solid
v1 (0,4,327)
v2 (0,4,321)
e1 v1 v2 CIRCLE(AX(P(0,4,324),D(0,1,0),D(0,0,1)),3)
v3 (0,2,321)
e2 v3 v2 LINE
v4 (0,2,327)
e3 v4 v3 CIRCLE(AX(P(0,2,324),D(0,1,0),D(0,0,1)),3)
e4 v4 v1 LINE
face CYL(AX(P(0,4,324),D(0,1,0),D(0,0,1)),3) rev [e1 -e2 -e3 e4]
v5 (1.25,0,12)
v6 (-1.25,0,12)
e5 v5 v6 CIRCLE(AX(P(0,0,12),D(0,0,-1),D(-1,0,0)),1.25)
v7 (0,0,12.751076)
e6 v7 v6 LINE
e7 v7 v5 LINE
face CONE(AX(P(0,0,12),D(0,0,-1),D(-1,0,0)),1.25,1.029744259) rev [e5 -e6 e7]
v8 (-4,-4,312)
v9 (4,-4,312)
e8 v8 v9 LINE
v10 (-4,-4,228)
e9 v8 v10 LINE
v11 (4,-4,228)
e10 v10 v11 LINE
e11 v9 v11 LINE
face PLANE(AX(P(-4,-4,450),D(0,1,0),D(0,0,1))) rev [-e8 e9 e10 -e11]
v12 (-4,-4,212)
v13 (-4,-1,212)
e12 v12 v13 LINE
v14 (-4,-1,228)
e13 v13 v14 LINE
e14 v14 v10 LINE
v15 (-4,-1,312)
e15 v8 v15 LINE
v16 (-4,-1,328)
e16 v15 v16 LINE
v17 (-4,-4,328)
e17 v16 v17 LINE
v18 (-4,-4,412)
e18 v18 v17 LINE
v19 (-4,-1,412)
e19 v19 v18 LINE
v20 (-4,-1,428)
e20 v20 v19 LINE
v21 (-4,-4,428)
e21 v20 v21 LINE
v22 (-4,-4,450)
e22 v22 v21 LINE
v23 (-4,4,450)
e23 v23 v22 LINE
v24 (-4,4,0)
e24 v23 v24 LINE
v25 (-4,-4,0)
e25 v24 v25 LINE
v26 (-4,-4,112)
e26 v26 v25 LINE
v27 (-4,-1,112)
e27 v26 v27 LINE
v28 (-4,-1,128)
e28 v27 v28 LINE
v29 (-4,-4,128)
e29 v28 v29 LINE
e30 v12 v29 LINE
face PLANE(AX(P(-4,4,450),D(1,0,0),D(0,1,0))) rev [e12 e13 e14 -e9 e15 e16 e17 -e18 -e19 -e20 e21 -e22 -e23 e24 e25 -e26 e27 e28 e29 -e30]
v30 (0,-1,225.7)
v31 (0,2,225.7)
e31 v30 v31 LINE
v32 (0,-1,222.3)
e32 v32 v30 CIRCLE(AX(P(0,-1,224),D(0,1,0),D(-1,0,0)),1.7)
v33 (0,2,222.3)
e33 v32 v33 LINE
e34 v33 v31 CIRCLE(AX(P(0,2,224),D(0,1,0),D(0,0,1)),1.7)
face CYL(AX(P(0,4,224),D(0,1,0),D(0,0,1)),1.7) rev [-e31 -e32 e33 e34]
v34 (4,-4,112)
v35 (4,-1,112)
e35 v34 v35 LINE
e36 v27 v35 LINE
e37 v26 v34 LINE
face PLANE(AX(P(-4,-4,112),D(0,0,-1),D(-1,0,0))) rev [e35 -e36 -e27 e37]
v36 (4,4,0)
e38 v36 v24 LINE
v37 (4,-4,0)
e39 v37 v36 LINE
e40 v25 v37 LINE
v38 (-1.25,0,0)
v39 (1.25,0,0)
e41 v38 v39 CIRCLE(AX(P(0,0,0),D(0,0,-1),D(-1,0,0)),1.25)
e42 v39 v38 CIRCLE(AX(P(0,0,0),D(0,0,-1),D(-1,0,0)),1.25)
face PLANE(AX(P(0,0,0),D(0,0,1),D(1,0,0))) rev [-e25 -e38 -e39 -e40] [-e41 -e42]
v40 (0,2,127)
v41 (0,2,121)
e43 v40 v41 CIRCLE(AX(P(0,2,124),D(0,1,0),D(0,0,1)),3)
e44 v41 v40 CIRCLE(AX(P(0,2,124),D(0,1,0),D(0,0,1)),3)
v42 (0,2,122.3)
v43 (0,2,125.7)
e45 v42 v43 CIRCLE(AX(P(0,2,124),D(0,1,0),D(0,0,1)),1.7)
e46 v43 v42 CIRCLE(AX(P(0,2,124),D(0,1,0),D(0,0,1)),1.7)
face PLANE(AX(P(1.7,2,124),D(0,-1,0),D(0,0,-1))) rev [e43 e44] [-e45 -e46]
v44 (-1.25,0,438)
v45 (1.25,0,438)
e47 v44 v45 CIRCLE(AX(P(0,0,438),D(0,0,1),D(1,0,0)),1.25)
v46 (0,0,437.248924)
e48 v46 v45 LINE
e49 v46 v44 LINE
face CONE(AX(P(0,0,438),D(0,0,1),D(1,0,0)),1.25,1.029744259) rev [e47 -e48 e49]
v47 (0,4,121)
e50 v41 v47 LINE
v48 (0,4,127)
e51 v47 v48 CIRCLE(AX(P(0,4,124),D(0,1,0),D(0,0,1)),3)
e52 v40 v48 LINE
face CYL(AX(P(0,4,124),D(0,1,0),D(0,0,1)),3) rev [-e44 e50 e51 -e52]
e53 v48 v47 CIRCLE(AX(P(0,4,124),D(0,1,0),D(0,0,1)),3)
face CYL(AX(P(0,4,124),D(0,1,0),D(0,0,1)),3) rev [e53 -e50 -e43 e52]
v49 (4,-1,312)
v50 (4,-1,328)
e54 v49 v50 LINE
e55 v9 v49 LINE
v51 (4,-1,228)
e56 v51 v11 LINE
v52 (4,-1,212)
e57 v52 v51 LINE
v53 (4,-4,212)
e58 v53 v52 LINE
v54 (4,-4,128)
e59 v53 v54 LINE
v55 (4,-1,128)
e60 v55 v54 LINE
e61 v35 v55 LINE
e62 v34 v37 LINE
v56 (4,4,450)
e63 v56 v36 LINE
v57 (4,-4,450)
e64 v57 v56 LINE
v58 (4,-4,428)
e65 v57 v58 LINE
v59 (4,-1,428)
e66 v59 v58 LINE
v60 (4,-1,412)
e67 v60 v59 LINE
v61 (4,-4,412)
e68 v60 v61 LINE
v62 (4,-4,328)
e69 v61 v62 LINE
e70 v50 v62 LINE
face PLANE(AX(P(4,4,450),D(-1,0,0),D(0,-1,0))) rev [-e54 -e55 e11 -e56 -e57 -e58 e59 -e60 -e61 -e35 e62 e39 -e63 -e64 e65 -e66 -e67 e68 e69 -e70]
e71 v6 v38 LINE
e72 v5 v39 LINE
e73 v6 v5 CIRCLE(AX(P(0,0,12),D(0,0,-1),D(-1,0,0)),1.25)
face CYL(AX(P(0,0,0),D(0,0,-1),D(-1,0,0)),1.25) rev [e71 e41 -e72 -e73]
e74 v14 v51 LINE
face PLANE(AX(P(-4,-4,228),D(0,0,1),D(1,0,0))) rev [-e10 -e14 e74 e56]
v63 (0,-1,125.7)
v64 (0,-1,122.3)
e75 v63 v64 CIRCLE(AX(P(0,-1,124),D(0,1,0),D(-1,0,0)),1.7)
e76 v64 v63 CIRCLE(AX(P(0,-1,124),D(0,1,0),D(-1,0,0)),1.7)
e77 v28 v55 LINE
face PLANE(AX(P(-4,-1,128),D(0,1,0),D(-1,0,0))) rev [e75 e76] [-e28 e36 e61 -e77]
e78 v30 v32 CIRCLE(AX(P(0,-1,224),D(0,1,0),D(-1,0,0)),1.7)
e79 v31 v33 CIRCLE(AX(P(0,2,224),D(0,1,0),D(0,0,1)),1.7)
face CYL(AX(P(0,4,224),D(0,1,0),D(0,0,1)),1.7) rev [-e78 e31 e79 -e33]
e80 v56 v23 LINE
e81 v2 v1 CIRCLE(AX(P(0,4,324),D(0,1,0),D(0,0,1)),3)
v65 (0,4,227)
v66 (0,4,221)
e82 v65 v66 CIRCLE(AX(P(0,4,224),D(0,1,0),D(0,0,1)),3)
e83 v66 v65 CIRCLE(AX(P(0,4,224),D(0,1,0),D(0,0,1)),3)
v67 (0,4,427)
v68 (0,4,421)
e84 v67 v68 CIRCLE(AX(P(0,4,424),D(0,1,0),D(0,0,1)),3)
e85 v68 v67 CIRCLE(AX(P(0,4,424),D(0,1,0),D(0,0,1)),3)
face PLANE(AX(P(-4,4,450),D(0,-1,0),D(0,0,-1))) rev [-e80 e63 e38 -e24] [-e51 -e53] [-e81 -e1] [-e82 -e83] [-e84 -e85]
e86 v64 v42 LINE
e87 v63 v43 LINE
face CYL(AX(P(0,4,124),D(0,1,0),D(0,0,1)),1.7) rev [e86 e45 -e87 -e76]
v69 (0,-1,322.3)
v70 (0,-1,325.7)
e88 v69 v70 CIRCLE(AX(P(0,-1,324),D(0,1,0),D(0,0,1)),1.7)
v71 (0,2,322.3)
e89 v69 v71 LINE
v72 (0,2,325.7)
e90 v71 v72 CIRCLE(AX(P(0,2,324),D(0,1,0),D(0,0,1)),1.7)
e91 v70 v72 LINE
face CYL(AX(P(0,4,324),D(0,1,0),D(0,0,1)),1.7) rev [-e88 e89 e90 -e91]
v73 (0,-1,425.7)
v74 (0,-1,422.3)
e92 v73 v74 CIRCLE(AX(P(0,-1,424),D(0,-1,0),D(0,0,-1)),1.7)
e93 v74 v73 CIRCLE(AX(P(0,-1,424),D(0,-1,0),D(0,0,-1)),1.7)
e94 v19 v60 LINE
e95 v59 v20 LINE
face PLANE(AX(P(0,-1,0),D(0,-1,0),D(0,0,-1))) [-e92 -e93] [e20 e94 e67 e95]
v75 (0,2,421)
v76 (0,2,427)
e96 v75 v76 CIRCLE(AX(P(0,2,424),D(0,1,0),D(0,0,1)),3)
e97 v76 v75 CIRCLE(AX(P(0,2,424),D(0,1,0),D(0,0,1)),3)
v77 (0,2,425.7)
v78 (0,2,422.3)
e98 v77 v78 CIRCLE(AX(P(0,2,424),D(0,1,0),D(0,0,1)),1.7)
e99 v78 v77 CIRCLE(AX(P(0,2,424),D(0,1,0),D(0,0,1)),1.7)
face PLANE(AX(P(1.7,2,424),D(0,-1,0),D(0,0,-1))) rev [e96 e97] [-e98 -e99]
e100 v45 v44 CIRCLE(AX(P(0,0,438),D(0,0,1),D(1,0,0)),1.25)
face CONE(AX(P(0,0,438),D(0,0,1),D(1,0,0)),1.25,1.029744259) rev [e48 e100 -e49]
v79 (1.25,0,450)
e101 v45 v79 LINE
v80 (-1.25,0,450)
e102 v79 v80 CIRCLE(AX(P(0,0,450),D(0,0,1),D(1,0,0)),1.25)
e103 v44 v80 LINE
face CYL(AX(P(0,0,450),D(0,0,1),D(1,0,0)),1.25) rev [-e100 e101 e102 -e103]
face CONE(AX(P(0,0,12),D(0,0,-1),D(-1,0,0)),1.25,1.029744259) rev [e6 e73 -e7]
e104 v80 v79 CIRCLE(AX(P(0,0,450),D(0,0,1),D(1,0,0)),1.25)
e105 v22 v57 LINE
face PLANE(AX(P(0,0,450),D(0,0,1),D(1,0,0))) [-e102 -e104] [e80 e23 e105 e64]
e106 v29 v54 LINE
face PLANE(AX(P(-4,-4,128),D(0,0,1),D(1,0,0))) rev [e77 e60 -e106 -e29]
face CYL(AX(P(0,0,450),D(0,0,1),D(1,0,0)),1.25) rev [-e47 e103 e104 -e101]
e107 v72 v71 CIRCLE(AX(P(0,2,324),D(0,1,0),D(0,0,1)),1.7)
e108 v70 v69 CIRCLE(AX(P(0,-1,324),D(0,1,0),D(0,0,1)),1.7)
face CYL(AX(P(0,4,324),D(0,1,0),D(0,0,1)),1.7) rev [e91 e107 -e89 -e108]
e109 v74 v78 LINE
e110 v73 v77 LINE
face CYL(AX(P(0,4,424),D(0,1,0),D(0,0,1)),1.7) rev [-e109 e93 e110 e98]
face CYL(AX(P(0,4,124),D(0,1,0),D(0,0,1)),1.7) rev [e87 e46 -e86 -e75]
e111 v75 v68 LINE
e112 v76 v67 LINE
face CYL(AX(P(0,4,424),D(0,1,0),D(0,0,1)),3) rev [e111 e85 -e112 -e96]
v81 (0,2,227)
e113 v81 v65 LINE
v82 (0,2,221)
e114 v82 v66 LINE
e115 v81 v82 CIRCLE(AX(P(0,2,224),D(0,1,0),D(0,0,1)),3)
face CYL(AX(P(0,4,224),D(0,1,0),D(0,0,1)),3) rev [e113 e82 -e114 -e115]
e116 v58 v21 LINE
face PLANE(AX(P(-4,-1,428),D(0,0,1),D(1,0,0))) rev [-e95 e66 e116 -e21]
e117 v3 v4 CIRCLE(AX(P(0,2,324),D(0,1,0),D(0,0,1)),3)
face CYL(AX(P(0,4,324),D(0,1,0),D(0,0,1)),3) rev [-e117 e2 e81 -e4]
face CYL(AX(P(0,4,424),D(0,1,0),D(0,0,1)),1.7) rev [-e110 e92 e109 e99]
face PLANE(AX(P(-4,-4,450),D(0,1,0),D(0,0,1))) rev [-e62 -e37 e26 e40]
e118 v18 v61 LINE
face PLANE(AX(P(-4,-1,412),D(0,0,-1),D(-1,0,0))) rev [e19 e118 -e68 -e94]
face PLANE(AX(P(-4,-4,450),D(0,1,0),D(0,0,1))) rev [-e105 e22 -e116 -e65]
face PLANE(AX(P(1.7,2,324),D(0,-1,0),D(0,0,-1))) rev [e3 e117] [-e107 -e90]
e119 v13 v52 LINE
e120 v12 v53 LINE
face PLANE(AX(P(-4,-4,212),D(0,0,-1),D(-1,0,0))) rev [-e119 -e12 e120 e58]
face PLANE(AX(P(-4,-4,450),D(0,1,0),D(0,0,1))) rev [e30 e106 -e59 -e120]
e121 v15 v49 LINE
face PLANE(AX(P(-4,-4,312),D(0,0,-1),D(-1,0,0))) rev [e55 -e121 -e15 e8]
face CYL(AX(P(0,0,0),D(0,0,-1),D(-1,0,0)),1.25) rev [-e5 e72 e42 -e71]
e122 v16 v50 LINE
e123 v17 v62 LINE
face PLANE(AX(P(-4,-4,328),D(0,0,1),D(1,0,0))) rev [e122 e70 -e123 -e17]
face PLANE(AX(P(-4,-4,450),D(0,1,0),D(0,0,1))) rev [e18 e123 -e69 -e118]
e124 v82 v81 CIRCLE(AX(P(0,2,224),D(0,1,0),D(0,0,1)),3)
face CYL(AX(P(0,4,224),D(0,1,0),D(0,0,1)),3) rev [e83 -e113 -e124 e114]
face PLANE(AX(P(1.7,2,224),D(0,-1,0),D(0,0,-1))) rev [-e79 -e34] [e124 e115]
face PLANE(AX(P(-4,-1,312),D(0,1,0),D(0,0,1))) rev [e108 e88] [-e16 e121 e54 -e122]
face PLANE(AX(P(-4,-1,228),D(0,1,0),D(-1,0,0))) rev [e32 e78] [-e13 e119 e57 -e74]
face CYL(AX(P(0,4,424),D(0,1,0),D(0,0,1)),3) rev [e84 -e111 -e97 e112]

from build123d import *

# Parameters (mm, degrees)
SKETCH_1_W                = 8
SKETCH_1_H                = 8
EXTRUDE_1_DEPTH           = 450
SKETCH_3_W                = 8
SKETCH_3_H                = 16
CUT_EXTRUDE_2_DEPTH       = 3
HOLE_WIZARD_M3_1_D        = 2.5
HOLE_WIZARD_M3_1_DEPTH    = 12
HOLE_WIZARD_M3_1_TIP      = 0.751075774
HOLE_WIZARD_M3_2_D        = 2.5
HOLE_WIZARD_M3_2_DEPTH    = 12
HOLE_WIZARD_M3_2_TIP      = 0.751075774
SKETCH_10_W               = 16
SKETCH_10_H               = 3
CUT_EXTRUDE_3_DEPTH       = 451.088880111
HOLE_WIZARD_1_D           = 3.4
HOLE_WIZARD_1_CBORE_D     = 6
HOLE_WIZARD_1_CBORE_DEPTH = 2


with BuildPart() as part:
    # 草图1 → 凸台-拉伸1 (new body)
    with BuildSketch(Plane.XY):
        Rectangle(SKETCH_1_W, SKETCH_1_H)
    extrude(amount=EXTRUDE_1_DEPTH)

    # 草图3 → 切除-拉伸2 (cut)
    with BuildSketch(Plane.XZ.offset(4)):
        with Locations((0, 420)):
            Rectangle(SKETCH_3_W, SKETCH_3_H)
    extrude(amount=-CUT_EXTRUDE_2_DEPTH, mode=Mode.SUBTRACT)

    # M3 螺纹孔1
    with Locations(Plane(origin=(0, 0, 0), x_dir=(-1, 0, 0), z_dir=(0, 0, -1))):
        with Locations((0, 0)):
            Hole(HOLE_WIZARD_M3_1_D / 2, depth=HOLE_WIZARD_M3_1_DEPTH)
            with Locations((0, 0, -(HOLE_WIZARD_M3_1_DEPTH + HOLE_WIZARD_M3_1_TIP / 2))):  # 118° drill point
                Cone(0, HOLE_WIZARD_M3_1_D / 2, HOLE_WIZARD_M3_1_TIP, mode=Mode.SUBTRACT)

    # M3 螺纹孔2
    with Locations(Plane.XY.offset(450)):
        with Locations((0, 0)):
            Hole(HOLE_WIZARD_M3_2_D / 2, depth=HOLE_WIZARD_M3_2_DEPTH)
            with Locations((0, 0, -(HOLE_WIZARD_M3_2_DEPTH + HOLE_WIZARD_M3_2_TIP / 2))):  # 118° drill point
                Cone(0, HOLE_WIZARD_M3_2_D / 2, HOLE_WIZARD_M3_2_TIP, mode=Mode.SUBTRACT)

    # 草图10 → 切除-拉伸3 (cut, through all)
    with BuildSketch(Plane(origin=(4, 0, 0), x_dir=(0, 0, -1), z_dir=(1, 0, 0))):
        with Locations((-320, -2.5)):
            Rectangle(SKETCH_10_W, SKETCH_10_H)
        with Locations((-220, -2.5)):
            Rectangle(SKETCH_10_W, SKETCH_10_H)
        with Locations((-120, -2.5)):
            Rectangle(SKETCH_10_W, SKETCH_10_H)
    extrude(amount=-CUT_EXTRUDE_3_DEPTH, mode=Mode.SUBTRACT)

    # 打孔尺寸根据内六角圆柱头螺钉的类型1 (through all)
    with Locations(Plane(origin=(0, 4, 0), x_dir=(1, 0, 0), z_dir=(0, 1, 0))):
        with Locations((0, -124), (0, -224), (0, -324), (0, -424)):
            CounterBoreHole(HOLE_WIZARD_1_D / 2, HOLE_WIZARD_1_CBORE_D / 2, HOLE_WIZARD_1_CBORE_DEPTH)


solid = part.part
